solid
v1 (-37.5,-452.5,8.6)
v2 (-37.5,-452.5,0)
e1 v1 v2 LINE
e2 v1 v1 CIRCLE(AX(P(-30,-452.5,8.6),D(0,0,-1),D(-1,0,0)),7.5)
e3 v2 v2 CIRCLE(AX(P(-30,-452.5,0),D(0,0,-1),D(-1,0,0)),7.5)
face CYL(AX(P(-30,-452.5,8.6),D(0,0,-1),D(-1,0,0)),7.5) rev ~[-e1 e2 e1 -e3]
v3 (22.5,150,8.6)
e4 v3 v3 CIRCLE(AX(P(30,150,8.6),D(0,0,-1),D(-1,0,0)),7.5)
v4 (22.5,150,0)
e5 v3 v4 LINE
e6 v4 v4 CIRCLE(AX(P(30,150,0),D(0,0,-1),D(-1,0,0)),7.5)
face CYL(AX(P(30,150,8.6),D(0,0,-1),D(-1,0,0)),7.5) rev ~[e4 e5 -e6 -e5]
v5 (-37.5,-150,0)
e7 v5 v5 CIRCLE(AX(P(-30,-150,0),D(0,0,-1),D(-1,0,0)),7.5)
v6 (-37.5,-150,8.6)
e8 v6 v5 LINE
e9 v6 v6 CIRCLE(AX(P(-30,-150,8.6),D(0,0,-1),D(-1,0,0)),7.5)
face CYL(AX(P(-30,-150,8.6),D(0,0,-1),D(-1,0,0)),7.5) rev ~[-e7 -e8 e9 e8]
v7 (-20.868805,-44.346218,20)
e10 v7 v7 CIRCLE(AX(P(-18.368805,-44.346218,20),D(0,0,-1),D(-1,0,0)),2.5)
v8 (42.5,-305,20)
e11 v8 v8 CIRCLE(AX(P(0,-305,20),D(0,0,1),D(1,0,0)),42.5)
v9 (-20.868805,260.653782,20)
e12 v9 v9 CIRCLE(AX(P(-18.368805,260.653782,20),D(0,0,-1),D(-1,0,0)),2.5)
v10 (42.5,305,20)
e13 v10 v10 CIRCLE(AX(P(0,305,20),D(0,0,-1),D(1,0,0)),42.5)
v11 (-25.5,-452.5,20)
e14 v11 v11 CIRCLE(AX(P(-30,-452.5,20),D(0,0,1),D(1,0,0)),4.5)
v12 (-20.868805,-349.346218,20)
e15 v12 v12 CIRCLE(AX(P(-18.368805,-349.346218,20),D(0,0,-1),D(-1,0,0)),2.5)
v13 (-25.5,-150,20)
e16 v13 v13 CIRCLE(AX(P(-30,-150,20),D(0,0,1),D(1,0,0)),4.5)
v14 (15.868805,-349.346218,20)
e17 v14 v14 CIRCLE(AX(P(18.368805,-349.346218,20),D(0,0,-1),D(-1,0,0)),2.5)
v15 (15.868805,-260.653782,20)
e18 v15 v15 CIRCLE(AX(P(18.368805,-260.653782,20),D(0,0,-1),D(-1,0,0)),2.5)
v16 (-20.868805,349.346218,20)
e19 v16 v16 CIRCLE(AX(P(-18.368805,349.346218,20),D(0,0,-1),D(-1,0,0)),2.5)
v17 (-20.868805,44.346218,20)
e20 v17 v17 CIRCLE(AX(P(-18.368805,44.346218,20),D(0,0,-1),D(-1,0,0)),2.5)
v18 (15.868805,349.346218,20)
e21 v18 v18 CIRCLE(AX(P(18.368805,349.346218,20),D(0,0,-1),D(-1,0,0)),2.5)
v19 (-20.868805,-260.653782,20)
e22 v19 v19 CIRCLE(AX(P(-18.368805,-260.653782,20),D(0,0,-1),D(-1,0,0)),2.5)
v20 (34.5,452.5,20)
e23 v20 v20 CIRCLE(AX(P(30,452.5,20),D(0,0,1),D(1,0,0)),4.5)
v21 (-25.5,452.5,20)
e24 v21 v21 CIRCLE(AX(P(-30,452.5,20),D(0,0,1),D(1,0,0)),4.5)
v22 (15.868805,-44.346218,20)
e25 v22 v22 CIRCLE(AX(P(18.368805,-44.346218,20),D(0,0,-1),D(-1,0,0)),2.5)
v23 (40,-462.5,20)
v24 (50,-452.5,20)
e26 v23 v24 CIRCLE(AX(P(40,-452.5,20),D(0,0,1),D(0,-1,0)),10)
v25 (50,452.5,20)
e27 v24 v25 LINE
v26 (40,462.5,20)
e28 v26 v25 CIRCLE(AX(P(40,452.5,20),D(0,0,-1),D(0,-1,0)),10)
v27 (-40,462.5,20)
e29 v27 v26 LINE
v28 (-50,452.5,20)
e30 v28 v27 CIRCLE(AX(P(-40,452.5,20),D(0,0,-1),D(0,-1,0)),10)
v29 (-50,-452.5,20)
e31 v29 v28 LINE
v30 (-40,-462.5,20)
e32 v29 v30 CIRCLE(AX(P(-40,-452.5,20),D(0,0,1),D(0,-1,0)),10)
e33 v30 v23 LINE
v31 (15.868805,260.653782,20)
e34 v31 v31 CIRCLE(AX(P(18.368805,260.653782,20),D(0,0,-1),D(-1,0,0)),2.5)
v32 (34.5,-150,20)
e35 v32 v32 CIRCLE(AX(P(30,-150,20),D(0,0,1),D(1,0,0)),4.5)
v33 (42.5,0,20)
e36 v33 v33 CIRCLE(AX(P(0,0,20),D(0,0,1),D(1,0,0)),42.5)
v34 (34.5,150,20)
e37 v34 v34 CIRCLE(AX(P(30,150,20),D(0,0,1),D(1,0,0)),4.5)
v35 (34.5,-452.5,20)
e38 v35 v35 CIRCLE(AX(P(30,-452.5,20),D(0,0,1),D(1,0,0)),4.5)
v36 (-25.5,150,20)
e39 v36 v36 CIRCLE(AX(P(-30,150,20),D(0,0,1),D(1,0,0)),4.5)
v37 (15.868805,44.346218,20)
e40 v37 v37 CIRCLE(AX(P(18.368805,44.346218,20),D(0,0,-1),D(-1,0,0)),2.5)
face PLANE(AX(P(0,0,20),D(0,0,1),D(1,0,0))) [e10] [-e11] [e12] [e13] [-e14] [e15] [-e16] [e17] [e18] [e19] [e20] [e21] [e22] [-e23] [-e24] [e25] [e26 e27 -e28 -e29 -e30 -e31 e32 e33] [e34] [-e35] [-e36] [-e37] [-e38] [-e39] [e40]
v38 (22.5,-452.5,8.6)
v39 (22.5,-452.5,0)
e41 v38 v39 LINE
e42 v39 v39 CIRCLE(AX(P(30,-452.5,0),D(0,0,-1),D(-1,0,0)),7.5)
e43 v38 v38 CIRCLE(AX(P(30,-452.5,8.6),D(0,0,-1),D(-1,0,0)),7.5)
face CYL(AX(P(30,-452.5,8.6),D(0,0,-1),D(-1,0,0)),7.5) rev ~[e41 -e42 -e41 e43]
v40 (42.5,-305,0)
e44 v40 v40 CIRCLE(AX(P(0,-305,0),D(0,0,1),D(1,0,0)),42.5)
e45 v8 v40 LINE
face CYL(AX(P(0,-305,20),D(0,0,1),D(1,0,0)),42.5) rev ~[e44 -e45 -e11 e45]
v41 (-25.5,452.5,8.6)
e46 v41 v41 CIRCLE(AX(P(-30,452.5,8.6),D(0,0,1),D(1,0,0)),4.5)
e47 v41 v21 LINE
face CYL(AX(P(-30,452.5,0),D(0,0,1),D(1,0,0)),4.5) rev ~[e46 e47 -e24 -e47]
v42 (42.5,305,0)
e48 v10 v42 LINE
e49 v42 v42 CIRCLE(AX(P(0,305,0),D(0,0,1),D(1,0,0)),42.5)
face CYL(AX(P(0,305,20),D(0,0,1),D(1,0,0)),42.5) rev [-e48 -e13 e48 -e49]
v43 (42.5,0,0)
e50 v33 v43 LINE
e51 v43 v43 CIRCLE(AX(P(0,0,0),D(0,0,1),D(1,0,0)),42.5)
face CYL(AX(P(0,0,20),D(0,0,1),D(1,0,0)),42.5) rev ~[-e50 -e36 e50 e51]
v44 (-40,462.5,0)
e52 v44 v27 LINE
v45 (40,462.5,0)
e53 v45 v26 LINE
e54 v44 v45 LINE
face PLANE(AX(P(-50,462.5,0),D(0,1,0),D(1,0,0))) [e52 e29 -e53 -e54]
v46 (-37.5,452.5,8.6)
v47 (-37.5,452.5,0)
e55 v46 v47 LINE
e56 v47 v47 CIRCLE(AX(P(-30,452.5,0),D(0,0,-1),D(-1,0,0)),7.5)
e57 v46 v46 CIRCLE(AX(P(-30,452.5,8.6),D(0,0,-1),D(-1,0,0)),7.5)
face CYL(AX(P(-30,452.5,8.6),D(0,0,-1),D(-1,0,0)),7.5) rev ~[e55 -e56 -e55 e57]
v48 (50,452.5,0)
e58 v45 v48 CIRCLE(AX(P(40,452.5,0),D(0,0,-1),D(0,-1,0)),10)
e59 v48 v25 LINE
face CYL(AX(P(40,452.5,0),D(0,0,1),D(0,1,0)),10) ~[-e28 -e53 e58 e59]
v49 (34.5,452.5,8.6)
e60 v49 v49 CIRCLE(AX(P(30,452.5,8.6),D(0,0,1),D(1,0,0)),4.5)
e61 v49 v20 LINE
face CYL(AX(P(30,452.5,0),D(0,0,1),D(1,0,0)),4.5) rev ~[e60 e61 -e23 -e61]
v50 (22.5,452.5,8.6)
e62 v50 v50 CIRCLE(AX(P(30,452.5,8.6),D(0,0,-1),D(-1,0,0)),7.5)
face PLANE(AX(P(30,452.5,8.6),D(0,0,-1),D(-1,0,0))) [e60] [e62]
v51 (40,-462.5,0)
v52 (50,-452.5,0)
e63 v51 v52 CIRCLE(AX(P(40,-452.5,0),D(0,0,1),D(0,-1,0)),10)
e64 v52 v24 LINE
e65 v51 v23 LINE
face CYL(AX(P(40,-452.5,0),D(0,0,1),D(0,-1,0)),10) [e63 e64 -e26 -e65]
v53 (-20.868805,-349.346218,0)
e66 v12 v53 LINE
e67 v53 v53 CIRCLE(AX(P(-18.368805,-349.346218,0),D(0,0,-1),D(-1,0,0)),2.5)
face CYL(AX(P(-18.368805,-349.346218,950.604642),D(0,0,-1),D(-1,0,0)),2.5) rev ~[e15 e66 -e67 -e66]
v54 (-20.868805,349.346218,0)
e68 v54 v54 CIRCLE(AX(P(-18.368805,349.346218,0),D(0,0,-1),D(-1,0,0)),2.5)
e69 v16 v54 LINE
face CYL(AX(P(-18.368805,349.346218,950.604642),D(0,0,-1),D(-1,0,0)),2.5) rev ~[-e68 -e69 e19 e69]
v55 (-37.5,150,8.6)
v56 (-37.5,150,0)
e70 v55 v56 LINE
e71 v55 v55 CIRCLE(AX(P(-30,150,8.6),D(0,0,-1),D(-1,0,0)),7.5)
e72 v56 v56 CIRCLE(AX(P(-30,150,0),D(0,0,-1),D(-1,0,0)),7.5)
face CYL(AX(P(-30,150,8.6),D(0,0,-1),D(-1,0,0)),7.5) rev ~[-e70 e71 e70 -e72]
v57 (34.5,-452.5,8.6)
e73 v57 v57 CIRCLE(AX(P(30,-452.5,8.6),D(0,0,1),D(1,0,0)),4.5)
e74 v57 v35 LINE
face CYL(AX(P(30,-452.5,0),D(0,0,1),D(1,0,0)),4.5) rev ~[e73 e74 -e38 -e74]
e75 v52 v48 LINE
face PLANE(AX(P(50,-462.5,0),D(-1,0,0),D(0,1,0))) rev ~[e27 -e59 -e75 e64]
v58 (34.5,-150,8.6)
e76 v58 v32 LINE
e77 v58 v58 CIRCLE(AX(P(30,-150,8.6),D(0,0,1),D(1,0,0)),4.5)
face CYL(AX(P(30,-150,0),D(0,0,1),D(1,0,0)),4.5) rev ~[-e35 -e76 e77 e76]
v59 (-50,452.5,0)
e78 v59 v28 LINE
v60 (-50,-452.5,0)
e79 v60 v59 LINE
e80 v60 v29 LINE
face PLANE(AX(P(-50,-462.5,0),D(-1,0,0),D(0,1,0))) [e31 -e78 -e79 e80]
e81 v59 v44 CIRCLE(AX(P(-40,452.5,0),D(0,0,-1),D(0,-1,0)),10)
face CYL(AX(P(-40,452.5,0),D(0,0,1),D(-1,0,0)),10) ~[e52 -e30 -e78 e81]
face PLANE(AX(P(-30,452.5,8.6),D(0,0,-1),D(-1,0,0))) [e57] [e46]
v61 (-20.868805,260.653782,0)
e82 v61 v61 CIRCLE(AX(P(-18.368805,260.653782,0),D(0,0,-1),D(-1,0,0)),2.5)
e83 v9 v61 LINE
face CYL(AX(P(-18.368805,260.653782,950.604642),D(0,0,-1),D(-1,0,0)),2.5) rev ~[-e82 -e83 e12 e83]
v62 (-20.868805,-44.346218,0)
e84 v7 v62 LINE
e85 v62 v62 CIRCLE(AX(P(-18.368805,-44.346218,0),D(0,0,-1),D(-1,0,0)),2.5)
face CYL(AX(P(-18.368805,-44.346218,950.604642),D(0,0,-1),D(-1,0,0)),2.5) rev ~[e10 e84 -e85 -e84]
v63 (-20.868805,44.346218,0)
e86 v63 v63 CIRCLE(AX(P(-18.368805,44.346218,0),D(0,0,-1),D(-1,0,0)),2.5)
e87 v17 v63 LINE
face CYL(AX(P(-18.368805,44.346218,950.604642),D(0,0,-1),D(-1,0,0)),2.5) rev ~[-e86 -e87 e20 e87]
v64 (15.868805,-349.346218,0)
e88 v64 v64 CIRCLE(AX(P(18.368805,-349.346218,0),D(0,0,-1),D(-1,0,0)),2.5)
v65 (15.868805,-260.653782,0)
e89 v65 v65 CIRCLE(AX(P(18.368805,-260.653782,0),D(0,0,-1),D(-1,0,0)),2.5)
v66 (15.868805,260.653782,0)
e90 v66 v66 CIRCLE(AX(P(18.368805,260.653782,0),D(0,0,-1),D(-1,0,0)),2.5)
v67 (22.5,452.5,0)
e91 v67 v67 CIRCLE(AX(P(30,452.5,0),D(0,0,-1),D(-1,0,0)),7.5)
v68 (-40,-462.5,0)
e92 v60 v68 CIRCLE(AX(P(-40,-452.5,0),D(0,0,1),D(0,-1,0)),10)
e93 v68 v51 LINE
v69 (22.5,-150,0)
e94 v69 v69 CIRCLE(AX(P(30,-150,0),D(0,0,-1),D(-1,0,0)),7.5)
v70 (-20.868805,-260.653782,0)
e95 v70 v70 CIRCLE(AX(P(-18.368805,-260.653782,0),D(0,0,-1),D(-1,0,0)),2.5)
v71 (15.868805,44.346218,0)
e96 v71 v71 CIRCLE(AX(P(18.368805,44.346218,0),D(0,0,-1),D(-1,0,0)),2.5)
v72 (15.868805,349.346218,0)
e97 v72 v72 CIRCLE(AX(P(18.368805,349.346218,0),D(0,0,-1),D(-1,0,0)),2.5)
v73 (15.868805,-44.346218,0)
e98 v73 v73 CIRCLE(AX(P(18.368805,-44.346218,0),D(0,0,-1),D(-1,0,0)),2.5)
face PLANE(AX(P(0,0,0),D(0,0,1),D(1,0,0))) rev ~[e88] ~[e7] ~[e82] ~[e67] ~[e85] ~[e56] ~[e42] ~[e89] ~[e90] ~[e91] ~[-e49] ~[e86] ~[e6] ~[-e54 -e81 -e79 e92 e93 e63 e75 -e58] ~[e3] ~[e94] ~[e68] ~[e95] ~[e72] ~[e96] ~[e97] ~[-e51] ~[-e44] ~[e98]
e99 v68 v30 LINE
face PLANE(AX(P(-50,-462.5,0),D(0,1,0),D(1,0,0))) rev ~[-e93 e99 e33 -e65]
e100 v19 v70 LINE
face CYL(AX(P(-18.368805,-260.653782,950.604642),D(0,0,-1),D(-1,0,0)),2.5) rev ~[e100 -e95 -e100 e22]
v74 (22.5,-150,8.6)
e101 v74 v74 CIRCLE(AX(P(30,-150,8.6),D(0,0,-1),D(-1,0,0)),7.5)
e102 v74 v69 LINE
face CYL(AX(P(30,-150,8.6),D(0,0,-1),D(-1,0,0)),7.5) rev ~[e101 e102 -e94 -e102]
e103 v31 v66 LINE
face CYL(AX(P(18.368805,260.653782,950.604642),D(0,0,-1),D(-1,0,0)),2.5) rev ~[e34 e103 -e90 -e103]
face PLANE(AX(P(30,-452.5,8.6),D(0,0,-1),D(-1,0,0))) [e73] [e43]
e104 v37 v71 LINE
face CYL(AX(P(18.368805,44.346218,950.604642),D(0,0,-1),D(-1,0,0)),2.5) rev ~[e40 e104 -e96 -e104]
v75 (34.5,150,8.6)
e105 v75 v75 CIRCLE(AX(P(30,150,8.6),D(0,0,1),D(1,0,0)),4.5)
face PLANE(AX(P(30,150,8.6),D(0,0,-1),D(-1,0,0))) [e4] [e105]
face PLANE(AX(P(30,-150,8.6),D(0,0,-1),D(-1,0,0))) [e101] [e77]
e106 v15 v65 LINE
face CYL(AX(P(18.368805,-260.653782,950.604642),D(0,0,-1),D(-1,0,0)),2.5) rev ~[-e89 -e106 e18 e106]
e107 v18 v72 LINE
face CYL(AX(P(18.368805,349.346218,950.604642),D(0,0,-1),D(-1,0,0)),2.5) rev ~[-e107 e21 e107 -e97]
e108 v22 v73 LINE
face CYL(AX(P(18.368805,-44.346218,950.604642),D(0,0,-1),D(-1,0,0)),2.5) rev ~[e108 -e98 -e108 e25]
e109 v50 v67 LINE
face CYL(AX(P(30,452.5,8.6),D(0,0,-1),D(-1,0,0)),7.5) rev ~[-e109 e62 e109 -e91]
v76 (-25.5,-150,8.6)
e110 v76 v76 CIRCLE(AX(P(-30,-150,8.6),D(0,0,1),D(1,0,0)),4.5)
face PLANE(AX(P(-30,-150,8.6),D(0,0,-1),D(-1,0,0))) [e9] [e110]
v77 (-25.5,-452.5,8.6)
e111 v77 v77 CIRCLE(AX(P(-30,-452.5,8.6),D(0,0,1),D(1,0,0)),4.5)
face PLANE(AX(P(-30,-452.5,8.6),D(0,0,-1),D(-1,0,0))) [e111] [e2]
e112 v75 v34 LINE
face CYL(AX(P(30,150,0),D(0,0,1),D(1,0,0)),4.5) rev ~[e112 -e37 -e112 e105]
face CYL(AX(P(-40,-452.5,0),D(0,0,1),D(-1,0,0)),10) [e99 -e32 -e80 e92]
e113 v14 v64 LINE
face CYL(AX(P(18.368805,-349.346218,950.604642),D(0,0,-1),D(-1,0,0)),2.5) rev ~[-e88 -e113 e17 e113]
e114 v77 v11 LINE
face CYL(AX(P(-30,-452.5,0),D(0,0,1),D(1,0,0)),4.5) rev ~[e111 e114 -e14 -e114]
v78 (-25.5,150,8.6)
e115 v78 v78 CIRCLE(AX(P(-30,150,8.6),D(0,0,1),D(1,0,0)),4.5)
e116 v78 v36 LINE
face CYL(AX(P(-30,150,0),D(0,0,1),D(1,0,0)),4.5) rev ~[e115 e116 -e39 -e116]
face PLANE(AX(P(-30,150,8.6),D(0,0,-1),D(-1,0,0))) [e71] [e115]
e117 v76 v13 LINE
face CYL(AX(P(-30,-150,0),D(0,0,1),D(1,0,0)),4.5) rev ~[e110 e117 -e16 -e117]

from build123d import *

# Parameters (mm, degrees)
SKETCH_1_W                   = 100
SKETCH_1_H                   = 925
EXTRUDE_1_DEPTH              = 20
HOLE_WIZARD_M6_2_D           = 5
SKETCH_11_R                  = 42.5
CUT_EXTRUDE_1_DEPTH          = 466.624580537
HOLE_WIZARD_M8_2_D           = 9
HOLE_WIZARD_M8_2_CBORE_D     = 15
HOLE_WIZARD_M8_2_CBORE_DEPTH = 8.6
FILLET_2_R                   = 10
SKETCH_14_R                  = 42.5
CUT_EXTRUDE_2_DEPTH          = 466.624580537
HOLE_WIZARD_M6_3_D           = 5


with BuildPart() as part:
    # 草图1 → 凸台-拉伸1 (new body)
    with BuildSketch(Plane.XY):
        Rectangle(SKETCH_1_W, SKETCH_1_H)
    extrude(amount=EXTRUDE_1_DEPTH)

    # M6 螺纹孔2 (through all)
    with Locations(Plane.XY.offset(20)):
        with Locations((-18.368804754, -260.653782439), (18.368804754, -260.653782439), (18.368804754, -349.346217561), (-18.368804754, -349.346217561), (18.368804754, 349.346217561), (-18.368804754, 349.346217561), (18.368804754, 260.653782439), (-18.368804754, 260.653782439)):
            Hole(HOLE_WIZARD_M6_2_D / 2)

    # 草图11 → 切除-拉伸1 (cut, through all)
    with BuildSketch(Plane.XY.offset(20)):
        with Locations((0, -305)):
            Circle(SKETCH_11_R)
    cut_extrude_1 = extrude(amount=-CUT_EXTRUDE_1_DEPTH, mode=Mode.SUBTRACT)

    # M8 六角凹头螺钉的柱形沉头孔2 (through all)
    with Locations(Plane(origin=(0, 0, 0), x_dir=(-1, 0, 0), z_dir=(0, 0, -1))):
        with Locations((-30, -452.5), (30, -452.5), (-30, -150), (30, -150), (30, 150), (-30, 150), (30, 452.5), (-30, 452.5)):
            CounterBoreHole(HOLE_WIZARD_M8_2_D / 2, HOLE_WIZARD_M8_2_CBORE_D / 2, HOLE_WIZARD_M8_2_CBORE_DEPTH)

    # 镜向10: 切除-拉伸1 across plane
    add(cut_extrude_1.mirror(Plane.ZX), mode=Mode.SUBTRACT)

    # 圆角2
    fillet_2_edges = [part.edges().sort_by_distance(p)[0] for p in [
        (50, -462.5, 10),
        (-50, -462.5, 10),
        (-50, 462.5, 10),
        (50, 462.5, 10),
    ]]
    fillet(fillet_2_edges, radius=FILLET_2_R)

    # 草图14 → 切除-拉伸2 (cut, through all)
    with BuildSketch(Plane.XY.offset(20)):
        Circle(SKETCH_14_R)
    extrude(amount=-CUT_EXTRUDE_2_DEPTH, mode=Mode.SUBTRACT)

    # M6 螺纹孔3 (through all)
    with Locations(Plane.XY.offset(20)):
        with Locations((-18.368804754, 44.346217561), (18.368804754, 44.346217561), (18.368804754, -44.346217561), (-18.368804754, -44.346217561)):
            Hole(HOLE_WIZARD_M6_3_D / 2)


solid = part.part
